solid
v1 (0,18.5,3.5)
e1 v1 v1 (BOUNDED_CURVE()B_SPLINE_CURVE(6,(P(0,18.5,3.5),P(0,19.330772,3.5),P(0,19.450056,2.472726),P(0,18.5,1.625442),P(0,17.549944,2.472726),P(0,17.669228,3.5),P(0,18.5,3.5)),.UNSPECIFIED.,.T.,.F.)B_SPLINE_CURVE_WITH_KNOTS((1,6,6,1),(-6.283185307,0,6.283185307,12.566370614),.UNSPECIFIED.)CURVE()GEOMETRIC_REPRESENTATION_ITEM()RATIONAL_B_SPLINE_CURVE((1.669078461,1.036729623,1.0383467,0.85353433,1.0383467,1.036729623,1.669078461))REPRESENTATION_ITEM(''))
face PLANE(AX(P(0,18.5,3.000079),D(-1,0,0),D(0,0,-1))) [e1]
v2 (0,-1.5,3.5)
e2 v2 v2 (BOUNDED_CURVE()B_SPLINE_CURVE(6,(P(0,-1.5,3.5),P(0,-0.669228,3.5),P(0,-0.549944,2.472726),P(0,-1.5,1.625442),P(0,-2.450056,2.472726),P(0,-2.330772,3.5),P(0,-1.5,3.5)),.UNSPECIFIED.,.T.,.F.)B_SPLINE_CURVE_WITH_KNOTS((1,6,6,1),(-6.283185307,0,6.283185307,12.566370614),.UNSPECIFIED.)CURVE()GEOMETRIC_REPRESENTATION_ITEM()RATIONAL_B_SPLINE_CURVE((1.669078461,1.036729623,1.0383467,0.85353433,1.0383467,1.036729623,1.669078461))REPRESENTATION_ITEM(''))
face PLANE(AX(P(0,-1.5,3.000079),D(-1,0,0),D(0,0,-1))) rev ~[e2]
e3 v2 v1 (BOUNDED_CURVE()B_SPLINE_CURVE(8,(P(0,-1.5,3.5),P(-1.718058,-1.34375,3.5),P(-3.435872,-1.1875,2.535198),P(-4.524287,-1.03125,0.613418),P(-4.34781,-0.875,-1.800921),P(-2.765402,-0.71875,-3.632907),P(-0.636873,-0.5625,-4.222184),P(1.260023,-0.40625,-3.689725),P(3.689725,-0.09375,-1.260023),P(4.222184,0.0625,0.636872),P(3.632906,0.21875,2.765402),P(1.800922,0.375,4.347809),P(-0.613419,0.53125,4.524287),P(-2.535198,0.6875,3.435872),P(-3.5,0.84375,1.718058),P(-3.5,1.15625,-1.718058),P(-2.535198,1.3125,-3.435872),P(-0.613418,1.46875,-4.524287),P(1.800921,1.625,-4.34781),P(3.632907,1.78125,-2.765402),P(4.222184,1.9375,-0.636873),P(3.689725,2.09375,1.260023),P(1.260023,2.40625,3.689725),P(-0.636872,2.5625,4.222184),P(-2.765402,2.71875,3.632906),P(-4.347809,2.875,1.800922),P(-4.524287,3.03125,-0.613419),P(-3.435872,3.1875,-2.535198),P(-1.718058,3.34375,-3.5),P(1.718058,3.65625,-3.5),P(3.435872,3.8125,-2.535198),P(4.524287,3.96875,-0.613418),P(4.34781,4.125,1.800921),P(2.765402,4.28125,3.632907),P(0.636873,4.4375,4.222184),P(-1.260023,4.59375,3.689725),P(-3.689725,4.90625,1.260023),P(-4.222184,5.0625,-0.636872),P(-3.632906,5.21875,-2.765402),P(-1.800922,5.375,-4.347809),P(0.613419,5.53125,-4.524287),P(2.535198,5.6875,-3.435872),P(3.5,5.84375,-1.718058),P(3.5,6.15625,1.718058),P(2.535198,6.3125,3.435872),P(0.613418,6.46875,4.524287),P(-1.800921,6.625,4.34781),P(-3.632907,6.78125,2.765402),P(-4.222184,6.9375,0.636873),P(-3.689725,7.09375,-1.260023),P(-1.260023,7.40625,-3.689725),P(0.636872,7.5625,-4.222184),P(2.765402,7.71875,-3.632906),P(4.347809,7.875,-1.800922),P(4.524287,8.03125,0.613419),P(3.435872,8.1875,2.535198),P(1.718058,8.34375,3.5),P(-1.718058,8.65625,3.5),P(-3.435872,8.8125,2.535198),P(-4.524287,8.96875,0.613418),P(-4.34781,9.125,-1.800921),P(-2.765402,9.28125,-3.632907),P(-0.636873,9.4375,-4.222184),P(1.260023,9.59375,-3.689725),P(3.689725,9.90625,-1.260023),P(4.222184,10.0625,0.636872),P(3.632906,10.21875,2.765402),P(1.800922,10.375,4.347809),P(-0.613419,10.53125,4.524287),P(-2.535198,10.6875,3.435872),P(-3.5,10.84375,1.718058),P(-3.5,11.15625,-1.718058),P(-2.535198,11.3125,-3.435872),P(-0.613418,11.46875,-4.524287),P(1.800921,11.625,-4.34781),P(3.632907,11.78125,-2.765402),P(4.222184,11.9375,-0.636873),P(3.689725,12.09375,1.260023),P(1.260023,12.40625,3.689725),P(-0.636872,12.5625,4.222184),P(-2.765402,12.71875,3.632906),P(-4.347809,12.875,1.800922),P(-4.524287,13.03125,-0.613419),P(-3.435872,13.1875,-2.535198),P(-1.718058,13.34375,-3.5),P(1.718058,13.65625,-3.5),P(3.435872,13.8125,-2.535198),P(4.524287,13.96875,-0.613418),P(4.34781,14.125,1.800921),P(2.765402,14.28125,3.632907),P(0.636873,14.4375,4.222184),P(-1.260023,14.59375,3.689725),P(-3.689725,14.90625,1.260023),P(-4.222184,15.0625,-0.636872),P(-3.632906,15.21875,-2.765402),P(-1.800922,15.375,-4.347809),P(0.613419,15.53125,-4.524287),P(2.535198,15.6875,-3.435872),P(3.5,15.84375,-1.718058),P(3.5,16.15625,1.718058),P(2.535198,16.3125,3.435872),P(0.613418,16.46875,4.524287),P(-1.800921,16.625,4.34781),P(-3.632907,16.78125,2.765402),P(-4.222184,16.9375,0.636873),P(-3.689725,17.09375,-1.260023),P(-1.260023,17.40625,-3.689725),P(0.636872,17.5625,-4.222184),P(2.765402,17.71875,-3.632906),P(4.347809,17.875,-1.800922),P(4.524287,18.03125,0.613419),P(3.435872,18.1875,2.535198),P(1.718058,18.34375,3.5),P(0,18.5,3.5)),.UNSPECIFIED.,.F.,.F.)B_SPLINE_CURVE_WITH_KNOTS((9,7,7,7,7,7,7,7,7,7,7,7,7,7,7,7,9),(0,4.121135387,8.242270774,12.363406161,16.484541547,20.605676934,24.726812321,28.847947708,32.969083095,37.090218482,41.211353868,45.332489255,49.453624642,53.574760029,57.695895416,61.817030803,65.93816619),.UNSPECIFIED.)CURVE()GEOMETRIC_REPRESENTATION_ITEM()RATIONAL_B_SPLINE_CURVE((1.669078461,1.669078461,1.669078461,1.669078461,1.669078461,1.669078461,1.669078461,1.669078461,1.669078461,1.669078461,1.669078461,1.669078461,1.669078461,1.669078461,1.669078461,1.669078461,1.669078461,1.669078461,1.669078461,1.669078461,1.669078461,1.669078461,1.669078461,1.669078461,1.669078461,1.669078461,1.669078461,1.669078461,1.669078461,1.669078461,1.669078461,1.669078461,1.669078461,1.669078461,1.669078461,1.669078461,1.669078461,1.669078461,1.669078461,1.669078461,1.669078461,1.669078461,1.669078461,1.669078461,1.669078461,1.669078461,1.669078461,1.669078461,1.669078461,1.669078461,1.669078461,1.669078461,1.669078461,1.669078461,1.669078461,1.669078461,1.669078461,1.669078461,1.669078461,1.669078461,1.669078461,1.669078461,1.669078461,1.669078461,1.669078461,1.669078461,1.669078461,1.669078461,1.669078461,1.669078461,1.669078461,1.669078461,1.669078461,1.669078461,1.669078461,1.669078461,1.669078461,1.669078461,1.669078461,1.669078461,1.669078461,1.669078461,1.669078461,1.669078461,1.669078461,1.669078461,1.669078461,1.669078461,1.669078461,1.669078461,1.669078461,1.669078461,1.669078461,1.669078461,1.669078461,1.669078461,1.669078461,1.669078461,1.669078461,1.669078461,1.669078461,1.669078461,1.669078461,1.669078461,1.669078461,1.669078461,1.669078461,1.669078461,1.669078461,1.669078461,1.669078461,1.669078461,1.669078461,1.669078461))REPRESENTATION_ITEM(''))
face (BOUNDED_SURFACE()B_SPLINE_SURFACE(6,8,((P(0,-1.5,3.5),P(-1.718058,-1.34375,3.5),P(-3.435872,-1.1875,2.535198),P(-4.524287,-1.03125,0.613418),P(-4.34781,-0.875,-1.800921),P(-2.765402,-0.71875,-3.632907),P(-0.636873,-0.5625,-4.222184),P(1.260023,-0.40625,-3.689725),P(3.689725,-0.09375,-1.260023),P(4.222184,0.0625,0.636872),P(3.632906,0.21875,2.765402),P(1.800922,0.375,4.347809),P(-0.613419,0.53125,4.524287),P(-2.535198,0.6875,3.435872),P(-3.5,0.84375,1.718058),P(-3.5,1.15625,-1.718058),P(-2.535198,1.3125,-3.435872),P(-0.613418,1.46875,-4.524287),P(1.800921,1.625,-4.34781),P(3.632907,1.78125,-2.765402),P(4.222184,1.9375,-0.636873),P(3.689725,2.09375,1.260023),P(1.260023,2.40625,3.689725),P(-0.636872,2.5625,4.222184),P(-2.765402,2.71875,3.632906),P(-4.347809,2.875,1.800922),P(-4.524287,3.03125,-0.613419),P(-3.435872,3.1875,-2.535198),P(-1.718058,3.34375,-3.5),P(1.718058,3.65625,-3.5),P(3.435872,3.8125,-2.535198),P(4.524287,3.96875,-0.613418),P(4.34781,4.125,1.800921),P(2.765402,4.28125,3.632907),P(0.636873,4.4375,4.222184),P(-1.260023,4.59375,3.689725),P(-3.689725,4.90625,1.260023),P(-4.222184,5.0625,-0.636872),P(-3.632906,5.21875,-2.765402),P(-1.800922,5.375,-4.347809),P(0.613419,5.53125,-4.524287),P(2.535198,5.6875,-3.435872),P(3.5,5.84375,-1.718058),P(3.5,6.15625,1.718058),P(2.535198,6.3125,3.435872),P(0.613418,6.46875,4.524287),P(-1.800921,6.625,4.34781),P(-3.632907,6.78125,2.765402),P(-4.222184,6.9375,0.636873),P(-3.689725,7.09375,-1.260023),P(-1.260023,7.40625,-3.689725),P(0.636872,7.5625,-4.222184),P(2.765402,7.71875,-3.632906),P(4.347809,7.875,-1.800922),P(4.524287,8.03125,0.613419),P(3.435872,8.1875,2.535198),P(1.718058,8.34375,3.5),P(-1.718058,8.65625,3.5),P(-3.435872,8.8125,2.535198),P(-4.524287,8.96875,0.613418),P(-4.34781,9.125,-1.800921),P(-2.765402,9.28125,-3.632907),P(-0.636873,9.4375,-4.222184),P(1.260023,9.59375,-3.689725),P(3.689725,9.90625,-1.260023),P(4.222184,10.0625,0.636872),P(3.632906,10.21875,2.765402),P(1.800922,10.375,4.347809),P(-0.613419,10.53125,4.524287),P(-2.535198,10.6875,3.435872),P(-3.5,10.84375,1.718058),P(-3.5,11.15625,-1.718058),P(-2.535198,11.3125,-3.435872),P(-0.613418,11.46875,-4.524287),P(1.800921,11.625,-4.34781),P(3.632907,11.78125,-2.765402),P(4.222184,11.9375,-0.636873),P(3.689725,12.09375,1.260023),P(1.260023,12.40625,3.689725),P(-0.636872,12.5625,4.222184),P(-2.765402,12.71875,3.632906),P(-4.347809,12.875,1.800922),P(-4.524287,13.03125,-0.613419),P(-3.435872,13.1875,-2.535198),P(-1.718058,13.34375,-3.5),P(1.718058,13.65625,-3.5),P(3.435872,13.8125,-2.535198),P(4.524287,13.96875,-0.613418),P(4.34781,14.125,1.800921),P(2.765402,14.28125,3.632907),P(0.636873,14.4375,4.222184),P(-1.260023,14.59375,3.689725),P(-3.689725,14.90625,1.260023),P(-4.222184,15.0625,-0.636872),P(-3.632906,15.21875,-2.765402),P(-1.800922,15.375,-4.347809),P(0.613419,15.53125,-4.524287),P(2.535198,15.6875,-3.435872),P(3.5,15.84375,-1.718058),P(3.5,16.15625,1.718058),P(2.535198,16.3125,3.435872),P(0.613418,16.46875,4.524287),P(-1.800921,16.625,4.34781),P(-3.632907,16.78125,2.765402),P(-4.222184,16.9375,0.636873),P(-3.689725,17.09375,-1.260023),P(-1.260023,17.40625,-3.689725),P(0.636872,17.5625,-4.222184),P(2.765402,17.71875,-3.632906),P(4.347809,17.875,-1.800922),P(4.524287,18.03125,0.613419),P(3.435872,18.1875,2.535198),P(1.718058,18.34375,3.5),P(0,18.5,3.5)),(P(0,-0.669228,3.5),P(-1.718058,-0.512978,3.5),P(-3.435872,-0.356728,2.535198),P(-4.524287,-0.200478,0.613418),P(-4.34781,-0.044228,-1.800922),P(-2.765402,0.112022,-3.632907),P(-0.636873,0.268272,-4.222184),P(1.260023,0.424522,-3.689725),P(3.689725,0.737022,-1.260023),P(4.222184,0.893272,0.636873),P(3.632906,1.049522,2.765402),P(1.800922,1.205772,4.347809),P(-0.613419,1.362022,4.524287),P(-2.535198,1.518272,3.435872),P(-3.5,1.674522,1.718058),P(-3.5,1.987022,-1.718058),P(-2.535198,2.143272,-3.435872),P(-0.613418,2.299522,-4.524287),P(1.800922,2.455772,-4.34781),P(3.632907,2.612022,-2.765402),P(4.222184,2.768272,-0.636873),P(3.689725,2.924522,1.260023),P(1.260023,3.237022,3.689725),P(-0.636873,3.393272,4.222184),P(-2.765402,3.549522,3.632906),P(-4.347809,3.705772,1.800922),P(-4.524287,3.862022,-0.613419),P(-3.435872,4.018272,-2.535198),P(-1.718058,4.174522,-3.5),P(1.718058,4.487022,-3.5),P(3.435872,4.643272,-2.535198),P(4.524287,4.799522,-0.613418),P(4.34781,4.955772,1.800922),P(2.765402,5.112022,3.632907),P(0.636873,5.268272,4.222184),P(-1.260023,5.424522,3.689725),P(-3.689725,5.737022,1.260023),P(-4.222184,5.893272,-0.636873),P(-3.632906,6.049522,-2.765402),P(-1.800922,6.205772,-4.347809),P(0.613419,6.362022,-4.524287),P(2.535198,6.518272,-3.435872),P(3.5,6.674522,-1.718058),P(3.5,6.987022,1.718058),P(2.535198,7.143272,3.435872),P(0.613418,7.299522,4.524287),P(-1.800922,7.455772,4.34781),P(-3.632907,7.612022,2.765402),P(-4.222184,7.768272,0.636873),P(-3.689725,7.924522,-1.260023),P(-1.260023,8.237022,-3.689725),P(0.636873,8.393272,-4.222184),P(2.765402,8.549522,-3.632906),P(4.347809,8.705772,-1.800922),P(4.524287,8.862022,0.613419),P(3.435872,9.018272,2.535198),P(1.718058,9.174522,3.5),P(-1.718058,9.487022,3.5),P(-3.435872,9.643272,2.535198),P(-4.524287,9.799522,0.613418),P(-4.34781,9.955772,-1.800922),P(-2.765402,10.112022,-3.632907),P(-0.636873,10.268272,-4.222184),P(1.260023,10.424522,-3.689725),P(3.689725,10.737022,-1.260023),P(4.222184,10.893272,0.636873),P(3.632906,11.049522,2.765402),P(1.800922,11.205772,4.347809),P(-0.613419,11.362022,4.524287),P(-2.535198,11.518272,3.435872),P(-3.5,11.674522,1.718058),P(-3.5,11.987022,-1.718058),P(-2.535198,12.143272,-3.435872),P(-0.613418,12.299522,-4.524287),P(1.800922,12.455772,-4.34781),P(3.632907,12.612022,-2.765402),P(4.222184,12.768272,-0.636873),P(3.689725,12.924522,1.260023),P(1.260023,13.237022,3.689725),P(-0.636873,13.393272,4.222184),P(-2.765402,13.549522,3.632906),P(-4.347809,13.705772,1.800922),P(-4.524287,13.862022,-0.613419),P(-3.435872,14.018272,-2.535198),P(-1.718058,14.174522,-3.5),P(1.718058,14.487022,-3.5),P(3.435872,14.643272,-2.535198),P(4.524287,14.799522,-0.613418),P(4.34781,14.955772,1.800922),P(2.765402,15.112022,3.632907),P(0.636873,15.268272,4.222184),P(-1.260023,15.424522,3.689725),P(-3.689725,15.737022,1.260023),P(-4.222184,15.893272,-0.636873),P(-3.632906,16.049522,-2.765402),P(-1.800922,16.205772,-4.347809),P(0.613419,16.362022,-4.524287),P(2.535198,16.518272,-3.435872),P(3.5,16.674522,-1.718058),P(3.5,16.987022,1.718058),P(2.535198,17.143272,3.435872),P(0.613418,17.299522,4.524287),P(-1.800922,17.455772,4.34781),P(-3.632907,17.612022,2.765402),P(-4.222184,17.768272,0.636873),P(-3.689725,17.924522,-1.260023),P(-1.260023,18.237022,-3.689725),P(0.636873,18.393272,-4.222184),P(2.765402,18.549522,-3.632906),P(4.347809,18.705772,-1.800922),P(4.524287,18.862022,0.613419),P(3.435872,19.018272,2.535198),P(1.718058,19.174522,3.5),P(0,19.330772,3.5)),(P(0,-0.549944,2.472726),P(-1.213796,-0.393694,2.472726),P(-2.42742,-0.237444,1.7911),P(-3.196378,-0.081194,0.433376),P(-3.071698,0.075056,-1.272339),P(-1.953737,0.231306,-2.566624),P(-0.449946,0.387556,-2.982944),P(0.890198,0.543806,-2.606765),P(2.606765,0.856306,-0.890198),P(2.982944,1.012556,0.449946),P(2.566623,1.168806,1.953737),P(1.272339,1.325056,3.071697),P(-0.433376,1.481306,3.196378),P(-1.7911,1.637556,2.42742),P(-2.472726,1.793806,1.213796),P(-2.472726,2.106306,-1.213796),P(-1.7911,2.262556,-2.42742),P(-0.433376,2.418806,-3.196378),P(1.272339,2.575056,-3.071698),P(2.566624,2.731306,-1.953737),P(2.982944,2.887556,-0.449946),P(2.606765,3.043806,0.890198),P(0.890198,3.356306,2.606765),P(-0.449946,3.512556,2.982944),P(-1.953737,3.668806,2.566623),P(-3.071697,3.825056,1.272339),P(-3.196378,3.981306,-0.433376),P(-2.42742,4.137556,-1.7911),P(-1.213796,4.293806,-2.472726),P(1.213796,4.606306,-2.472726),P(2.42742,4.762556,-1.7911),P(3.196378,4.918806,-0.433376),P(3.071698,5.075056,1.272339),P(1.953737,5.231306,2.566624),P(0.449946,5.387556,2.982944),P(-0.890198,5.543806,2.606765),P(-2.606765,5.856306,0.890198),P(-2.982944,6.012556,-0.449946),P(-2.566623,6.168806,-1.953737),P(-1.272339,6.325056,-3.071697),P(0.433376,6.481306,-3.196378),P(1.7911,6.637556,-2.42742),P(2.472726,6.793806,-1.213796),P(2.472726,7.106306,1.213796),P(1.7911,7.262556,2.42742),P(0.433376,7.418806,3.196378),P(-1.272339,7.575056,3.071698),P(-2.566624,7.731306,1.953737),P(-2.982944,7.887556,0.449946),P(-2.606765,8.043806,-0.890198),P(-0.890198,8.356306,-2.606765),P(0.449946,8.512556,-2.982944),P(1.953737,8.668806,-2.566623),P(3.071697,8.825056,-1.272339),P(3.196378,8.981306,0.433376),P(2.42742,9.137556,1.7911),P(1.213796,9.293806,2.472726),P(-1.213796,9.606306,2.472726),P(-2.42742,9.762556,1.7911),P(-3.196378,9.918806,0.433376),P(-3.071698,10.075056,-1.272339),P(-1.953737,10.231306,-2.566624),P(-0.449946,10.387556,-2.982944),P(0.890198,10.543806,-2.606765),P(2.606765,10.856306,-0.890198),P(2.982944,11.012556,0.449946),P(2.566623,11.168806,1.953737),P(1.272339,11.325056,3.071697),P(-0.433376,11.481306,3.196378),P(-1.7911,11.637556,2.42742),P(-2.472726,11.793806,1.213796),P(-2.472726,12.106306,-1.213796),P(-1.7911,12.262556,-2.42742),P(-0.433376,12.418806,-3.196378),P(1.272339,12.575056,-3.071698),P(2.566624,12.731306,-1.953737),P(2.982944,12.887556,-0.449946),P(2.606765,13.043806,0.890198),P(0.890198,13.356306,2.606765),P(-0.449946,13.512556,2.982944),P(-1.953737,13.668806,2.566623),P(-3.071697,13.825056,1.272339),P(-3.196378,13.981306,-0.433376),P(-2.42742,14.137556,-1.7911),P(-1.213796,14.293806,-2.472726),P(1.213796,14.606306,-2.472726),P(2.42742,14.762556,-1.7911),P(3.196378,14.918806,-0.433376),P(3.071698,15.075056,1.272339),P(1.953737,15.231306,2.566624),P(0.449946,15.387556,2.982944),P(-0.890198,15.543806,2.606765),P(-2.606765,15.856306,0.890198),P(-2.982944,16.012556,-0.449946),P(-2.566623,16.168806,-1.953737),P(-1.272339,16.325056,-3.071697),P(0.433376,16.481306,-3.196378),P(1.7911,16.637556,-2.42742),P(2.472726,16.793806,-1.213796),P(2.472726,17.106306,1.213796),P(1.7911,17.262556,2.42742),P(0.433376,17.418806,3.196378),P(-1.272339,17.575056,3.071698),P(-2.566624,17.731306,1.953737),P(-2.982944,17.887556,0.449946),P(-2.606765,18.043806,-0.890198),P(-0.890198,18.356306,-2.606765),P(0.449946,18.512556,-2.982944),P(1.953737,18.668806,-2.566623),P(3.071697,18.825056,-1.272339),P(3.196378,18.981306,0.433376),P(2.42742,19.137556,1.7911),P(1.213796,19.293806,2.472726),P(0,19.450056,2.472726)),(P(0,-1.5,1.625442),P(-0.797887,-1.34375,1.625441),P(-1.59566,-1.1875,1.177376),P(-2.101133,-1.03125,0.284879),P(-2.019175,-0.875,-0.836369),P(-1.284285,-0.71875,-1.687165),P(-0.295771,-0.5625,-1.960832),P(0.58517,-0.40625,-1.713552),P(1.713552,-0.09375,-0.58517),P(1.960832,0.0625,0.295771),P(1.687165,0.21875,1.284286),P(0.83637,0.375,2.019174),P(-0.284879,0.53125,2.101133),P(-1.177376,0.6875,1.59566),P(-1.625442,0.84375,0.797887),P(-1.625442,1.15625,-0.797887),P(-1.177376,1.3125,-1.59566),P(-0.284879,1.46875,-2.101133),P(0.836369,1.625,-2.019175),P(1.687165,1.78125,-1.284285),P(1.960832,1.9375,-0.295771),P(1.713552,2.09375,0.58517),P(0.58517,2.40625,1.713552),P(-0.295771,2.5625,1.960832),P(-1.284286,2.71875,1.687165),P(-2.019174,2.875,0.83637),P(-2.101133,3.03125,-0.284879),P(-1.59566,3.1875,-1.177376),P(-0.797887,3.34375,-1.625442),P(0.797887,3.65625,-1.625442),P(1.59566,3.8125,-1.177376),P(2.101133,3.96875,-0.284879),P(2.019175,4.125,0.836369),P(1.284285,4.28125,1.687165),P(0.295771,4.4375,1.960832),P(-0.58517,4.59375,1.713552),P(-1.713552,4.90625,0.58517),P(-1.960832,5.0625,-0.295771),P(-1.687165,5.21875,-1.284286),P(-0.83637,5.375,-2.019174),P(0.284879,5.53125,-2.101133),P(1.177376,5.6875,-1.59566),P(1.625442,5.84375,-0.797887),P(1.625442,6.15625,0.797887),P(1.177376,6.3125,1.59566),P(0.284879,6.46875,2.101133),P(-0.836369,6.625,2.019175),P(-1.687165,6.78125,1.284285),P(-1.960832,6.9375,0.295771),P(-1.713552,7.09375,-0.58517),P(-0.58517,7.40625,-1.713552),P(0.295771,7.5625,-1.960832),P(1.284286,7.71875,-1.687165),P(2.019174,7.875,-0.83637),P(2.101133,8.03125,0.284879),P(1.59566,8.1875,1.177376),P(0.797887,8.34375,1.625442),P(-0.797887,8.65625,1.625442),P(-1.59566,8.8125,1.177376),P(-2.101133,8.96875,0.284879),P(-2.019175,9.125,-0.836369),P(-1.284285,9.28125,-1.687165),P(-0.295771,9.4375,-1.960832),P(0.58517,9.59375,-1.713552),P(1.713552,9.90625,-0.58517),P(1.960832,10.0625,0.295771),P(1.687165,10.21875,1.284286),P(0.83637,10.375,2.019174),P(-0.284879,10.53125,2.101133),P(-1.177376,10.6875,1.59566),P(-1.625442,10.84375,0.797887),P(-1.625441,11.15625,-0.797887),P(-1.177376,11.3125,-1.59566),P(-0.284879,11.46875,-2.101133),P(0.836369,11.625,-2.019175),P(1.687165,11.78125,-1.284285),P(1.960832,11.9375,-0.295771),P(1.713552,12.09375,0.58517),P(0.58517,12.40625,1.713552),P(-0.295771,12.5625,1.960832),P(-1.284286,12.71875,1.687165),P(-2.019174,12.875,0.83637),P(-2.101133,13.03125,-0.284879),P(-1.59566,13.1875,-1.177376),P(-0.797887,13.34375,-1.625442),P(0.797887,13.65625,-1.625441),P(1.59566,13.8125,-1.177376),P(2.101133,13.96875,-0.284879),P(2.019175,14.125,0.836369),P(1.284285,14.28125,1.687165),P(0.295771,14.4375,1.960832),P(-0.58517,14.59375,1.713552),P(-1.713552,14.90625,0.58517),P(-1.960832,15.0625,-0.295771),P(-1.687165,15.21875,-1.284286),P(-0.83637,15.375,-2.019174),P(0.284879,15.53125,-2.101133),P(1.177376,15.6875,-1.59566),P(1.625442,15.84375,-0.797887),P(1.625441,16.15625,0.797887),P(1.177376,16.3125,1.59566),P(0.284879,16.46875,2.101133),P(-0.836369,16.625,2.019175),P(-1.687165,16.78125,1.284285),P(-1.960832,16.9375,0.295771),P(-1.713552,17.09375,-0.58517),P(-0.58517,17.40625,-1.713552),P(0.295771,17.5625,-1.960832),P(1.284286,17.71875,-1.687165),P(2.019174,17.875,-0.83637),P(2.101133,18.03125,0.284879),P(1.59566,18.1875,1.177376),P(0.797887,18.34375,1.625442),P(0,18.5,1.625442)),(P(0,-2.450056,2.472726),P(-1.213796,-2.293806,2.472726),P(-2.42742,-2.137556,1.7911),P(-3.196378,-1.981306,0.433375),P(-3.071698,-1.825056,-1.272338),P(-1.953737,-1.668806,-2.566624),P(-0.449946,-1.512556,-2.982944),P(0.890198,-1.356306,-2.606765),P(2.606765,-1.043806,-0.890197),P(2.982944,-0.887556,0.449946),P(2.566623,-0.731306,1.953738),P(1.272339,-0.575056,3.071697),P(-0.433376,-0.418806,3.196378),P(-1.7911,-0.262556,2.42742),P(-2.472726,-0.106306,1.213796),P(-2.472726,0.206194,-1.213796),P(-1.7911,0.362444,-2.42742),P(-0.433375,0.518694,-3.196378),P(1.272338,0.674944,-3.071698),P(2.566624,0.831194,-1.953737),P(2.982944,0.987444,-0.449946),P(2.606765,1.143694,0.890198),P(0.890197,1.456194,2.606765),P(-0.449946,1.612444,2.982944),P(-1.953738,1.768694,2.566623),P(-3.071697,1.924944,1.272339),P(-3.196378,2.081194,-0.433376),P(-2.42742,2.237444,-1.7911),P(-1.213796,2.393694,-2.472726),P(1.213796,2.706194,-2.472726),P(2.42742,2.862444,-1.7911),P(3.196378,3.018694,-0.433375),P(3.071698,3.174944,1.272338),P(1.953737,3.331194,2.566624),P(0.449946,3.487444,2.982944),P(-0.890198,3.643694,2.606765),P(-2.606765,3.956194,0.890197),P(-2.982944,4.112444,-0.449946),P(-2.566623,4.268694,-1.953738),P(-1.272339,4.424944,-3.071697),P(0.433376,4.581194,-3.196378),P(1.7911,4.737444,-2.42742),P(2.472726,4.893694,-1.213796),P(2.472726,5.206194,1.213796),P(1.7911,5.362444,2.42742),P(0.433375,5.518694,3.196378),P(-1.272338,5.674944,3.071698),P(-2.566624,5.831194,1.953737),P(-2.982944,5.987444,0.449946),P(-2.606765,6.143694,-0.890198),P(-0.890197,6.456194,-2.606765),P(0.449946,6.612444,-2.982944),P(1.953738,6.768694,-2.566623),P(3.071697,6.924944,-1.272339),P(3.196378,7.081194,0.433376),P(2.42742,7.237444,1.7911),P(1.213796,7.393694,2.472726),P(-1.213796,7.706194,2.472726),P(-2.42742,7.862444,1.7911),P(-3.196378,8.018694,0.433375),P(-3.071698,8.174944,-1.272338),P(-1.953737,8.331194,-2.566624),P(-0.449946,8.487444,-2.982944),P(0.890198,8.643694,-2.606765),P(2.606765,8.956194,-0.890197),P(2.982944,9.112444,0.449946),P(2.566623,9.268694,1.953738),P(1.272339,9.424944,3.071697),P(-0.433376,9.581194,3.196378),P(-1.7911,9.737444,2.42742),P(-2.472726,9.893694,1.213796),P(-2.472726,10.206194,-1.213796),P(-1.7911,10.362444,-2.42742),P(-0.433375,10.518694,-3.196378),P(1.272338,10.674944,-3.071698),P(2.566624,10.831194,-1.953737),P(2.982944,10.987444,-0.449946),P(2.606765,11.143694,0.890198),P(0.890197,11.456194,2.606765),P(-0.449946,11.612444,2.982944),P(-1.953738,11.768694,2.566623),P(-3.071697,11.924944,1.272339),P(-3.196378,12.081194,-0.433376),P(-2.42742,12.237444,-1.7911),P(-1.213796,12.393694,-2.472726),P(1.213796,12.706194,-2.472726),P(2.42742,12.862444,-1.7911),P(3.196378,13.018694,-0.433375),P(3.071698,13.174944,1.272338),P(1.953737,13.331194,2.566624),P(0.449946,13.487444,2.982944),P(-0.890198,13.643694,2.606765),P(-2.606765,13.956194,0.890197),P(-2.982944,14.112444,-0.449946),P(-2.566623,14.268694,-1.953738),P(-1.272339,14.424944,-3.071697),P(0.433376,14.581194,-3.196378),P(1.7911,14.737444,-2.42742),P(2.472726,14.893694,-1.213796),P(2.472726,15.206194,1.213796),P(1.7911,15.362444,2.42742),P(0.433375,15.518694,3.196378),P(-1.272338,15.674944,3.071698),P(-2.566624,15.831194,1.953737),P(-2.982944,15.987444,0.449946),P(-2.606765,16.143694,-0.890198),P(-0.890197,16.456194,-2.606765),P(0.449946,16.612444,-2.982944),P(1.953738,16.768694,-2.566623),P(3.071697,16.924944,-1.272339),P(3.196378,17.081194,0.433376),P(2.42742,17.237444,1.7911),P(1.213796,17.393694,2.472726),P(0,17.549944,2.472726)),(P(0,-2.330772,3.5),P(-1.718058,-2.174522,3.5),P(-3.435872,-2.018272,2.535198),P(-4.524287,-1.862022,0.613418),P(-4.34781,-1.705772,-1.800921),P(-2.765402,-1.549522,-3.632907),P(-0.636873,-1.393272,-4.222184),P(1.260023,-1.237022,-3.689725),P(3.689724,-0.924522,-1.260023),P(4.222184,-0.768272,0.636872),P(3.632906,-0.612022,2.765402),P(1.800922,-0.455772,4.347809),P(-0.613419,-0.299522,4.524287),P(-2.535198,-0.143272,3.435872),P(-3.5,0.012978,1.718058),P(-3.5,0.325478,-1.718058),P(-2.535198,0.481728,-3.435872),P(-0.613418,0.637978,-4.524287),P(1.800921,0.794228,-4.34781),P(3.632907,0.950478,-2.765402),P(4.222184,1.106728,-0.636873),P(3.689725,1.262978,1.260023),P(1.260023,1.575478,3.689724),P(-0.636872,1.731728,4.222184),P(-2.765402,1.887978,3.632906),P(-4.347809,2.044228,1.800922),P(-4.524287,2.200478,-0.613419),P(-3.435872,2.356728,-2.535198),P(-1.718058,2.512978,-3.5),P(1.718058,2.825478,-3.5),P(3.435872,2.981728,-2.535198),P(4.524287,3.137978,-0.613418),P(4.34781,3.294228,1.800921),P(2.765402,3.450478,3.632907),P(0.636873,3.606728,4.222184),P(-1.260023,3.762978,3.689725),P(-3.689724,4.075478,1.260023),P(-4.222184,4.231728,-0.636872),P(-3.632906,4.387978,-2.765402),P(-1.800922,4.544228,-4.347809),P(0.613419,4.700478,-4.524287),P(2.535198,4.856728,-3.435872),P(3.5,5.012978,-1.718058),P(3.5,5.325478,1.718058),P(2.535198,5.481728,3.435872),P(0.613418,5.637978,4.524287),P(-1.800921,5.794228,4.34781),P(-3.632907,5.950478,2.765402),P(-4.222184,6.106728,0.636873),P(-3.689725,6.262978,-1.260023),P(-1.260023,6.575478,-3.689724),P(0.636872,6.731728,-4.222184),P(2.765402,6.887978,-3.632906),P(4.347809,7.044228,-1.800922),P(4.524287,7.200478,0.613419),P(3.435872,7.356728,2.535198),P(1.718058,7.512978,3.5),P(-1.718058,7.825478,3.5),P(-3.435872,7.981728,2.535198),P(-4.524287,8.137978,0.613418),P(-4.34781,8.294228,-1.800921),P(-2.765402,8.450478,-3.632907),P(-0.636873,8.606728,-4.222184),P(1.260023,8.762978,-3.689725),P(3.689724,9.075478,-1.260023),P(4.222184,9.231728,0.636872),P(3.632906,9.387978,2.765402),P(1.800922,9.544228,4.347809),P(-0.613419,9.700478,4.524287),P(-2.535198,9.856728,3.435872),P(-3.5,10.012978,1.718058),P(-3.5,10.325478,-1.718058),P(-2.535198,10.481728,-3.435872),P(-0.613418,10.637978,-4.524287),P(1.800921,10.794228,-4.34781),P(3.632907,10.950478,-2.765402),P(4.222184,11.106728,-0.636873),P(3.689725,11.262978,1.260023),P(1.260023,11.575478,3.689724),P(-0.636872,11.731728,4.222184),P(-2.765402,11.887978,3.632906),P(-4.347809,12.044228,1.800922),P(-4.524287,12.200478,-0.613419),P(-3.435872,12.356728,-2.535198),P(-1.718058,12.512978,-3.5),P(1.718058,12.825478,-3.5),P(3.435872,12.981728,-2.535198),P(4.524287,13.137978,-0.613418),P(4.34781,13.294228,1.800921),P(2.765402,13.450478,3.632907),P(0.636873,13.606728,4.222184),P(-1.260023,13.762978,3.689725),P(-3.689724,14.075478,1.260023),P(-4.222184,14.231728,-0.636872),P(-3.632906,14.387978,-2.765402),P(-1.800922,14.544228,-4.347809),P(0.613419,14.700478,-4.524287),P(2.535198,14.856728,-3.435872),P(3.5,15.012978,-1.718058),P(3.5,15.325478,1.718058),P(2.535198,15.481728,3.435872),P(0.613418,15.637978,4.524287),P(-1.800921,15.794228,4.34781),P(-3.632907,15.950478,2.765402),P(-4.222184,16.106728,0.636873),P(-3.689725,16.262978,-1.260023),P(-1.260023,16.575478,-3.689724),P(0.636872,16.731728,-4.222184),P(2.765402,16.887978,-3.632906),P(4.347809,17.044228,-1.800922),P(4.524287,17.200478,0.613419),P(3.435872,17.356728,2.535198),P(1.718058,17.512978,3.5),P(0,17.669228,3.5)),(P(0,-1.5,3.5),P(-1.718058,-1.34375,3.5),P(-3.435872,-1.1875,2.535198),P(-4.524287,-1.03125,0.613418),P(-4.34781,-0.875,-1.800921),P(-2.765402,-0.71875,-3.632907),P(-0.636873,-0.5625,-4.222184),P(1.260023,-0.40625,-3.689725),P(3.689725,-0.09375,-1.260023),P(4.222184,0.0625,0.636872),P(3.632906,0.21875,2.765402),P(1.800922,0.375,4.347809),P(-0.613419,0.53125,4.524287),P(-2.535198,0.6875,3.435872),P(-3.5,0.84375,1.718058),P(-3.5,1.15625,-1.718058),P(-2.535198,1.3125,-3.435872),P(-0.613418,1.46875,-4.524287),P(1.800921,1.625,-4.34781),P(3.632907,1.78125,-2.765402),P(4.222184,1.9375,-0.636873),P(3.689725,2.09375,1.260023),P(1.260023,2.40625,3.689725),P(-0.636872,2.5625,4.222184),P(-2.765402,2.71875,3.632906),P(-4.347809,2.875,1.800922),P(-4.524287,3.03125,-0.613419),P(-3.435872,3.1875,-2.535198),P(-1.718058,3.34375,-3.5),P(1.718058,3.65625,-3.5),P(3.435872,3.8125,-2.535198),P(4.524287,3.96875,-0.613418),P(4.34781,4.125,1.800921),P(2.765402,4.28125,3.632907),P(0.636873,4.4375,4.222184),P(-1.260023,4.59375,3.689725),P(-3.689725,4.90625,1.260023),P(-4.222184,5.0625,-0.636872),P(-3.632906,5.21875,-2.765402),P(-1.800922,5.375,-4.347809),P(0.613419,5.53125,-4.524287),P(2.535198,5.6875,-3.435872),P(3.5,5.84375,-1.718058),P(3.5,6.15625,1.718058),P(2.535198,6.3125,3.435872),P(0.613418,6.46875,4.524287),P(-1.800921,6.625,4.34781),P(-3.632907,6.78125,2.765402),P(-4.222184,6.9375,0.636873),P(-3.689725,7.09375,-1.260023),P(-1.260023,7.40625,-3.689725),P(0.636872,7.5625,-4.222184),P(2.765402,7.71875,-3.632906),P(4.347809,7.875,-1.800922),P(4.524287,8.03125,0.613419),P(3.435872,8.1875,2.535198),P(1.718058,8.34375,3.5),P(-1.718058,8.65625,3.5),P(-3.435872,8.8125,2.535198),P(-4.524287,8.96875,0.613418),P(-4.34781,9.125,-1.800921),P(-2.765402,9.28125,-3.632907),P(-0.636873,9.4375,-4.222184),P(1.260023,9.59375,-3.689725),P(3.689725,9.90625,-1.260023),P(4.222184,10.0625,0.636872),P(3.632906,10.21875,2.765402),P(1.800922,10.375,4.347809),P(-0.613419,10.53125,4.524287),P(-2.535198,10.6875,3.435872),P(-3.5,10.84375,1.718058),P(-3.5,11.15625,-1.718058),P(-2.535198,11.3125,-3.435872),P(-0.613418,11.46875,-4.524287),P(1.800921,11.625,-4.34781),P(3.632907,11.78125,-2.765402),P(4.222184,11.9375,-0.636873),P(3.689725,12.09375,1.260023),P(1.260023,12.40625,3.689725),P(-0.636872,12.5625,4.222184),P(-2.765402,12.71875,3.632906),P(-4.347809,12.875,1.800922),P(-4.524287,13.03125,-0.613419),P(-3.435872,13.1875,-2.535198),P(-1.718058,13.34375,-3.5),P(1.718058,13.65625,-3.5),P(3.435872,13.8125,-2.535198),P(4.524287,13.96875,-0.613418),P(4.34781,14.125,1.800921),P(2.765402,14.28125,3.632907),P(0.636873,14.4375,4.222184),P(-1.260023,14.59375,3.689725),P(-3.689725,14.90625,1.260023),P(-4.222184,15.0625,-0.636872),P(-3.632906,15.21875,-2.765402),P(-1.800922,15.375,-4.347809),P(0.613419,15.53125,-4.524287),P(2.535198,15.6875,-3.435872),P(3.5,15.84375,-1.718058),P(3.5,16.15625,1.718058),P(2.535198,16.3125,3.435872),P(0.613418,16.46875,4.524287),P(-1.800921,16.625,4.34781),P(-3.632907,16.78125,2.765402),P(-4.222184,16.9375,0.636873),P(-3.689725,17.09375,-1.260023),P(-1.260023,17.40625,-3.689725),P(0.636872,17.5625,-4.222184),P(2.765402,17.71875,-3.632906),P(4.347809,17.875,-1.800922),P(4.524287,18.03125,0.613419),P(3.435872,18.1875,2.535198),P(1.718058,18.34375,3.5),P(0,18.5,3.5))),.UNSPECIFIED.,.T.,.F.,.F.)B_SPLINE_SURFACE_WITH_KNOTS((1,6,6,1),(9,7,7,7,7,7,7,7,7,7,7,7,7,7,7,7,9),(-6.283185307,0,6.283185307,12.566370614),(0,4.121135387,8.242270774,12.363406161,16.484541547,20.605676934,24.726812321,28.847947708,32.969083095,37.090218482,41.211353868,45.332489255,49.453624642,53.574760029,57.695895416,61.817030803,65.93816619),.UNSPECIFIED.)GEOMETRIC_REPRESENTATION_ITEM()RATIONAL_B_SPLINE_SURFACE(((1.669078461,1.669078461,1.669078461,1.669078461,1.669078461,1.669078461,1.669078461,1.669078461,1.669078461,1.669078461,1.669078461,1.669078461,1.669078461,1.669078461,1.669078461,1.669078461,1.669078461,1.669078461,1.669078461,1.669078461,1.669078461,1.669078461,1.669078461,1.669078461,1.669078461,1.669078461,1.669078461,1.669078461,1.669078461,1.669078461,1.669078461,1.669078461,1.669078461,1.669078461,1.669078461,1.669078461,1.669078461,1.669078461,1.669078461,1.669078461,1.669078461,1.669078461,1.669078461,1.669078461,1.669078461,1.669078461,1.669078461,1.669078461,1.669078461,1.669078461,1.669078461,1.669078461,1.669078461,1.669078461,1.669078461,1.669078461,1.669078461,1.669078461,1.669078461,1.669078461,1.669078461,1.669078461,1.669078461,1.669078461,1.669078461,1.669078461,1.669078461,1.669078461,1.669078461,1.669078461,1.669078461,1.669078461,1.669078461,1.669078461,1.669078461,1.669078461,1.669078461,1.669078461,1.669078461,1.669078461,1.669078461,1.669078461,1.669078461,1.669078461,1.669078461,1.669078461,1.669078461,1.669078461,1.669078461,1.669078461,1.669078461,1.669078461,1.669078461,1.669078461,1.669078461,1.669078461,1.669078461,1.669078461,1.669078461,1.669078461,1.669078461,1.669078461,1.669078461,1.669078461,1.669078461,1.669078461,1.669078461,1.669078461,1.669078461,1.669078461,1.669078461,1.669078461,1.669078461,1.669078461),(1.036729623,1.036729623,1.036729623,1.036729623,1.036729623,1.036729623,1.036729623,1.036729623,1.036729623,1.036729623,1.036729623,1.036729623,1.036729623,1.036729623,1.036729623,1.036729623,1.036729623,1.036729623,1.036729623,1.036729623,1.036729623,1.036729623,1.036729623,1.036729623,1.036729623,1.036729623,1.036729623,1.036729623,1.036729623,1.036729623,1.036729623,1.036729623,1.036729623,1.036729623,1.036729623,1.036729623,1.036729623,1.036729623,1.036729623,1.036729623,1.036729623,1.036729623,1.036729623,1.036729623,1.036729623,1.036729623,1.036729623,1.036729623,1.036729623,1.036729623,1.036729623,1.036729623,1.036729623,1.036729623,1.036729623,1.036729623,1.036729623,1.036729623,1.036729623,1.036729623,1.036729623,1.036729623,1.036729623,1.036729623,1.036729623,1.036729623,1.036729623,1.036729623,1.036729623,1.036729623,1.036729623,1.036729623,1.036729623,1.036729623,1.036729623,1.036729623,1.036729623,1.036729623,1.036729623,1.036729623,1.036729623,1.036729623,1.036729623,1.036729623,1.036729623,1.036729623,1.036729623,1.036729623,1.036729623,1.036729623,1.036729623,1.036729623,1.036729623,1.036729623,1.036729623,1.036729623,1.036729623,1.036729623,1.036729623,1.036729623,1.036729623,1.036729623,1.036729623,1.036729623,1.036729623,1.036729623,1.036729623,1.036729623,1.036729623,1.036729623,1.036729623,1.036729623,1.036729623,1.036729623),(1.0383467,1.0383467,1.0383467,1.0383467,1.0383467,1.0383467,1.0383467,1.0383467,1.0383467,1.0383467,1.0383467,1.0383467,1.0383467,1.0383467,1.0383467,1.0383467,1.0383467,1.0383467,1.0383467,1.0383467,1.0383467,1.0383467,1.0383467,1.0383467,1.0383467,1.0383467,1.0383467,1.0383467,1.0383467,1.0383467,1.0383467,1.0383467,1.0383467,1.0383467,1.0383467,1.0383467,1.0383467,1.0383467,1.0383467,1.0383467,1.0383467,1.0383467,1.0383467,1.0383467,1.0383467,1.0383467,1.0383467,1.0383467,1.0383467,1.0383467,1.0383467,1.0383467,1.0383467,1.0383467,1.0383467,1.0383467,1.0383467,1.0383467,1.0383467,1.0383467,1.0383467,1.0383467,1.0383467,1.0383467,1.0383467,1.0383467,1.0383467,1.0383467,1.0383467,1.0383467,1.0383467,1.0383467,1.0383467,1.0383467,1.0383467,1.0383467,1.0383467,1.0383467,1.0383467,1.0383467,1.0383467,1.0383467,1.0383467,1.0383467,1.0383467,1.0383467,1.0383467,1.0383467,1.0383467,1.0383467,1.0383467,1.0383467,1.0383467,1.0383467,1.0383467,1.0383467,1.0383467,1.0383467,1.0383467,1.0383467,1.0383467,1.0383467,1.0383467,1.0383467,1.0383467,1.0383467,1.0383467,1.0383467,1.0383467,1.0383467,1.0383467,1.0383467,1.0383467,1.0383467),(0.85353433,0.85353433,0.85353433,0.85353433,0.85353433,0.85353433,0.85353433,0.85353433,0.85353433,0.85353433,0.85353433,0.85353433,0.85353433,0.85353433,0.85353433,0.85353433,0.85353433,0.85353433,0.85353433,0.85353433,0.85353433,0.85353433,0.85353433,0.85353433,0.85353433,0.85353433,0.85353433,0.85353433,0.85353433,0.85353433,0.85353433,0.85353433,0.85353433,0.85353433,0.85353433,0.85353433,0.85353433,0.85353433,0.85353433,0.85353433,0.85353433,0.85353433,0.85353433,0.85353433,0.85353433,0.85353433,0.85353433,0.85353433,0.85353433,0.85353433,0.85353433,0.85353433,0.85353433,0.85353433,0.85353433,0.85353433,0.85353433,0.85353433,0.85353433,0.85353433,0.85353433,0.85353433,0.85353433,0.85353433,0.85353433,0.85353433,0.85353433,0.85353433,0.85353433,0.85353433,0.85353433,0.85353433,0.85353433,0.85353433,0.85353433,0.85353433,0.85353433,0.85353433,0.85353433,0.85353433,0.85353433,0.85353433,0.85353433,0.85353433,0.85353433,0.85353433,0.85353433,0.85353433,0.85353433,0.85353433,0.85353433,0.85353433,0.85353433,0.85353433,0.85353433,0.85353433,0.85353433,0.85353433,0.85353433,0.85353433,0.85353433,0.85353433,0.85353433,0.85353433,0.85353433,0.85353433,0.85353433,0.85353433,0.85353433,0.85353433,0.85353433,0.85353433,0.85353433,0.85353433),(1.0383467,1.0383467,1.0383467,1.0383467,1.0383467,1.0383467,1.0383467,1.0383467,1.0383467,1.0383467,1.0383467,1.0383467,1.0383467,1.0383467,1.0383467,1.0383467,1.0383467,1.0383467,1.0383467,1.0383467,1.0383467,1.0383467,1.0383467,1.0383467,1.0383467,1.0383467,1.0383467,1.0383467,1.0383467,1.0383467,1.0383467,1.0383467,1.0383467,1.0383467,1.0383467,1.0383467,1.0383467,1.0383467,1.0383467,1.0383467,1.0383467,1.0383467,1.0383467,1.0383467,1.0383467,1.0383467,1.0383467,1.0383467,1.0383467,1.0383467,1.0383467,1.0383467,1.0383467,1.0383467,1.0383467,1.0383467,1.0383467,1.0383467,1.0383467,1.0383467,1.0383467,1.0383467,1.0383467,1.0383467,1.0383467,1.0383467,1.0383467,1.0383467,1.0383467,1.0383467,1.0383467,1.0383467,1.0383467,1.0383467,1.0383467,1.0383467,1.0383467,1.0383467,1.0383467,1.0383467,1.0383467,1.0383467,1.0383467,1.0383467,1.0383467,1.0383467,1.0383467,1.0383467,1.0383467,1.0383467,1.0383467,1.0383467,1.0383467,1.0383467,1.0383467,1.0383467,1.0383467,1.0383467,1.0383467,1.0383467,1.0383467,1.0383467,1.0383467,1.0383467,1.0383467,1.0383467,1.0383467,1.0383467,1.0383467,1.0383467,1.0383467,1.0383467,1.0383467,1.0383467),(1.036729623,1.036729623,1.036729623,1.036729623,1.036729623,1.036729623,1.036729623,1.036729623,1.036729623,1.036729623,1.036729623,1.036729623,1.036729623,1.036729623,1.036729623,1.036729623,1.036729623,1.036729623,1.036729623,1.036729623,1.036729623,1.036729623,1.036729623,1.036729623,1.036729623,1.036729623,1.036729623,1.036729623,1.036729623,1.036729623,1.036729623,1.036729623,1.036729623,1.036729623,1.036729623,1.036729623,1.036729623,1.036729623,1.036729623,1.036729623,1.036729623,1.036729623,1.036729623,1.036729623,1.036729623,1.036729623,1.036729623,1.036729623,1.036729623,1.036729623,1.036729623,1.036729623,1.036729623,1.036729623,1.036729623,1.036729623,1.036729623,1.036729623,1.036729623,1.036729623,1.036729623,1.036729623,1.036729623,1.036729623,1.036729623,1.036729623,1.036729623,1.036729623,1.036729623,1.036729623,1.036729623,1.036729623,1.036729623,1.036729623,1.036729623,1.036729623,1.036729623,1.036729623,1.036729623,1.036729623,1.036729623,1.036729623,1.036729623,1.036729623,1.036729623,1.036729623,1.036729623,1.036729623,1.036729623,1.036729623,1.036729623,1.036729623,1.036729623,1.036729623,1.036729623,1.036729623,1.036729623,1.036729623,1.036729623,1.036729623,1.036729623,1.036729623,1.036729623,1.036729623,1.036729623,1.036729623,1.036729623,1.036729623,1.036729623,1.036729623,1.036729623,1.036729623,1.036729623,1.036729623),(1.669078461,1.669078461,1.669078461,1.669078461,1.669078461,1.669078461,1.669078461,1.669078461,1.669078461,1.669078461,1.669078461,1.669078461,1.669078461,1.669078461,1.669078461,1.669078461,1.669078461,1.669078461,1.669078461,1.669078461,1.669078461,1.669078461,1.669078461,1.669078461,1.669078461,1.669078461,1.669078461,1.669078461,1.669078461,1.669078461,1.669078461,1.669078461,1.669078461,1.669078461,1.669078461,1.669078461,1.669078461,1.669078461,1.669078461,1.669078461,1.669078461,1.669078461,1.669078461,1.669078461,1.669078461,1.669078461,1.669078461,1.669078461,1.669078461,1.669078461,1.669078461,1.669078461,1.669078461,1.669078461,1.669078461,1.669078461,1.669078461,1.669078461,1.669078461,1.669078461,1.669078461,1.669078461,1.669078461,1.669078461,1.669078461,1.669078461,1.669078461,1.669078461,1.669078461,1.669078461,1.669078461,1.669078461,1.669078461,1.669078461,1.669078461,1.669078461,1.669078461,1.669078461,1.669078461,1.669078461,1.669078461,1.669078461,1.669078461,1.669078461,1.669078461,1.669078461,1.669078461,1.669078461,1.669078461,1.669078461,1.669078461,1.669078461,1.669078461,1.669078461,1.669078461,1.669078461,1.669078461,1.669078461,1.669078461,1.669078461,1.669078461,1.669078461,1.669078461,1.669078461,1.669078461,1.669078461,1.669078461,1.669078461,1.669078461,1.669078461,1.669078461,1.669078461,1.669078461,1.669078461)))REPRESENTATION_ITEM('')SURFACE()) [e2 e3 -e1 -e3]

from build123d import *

# Parameters (mm, degrees)
SWEEP1_PITCH  = 2
SWEEP1_HEIGHT = 20
SWEEP1_RADIUS = 3
SKETCH1_R     = 0.5


with BuildPart() as part:
    # Sweep1: sweep along a helix
    with BuildLine() as sweep1_path:
        Helix(SWEEP1_PITCH, SWEEP1_HEIGHT, SWEEP1_RADIUS, center=(0, 0, 0), direction=(0, 1, 0), lefthand=True)
    # Sketch1 → Sweep1 (sweep)
    with BuildSketch(Plane.XY):
        with Locations((3, 0)):
            Circle(SKETCH1_R)
    sweep(path=sweep1_path.line, is_frenet=True)


solid = part.part
